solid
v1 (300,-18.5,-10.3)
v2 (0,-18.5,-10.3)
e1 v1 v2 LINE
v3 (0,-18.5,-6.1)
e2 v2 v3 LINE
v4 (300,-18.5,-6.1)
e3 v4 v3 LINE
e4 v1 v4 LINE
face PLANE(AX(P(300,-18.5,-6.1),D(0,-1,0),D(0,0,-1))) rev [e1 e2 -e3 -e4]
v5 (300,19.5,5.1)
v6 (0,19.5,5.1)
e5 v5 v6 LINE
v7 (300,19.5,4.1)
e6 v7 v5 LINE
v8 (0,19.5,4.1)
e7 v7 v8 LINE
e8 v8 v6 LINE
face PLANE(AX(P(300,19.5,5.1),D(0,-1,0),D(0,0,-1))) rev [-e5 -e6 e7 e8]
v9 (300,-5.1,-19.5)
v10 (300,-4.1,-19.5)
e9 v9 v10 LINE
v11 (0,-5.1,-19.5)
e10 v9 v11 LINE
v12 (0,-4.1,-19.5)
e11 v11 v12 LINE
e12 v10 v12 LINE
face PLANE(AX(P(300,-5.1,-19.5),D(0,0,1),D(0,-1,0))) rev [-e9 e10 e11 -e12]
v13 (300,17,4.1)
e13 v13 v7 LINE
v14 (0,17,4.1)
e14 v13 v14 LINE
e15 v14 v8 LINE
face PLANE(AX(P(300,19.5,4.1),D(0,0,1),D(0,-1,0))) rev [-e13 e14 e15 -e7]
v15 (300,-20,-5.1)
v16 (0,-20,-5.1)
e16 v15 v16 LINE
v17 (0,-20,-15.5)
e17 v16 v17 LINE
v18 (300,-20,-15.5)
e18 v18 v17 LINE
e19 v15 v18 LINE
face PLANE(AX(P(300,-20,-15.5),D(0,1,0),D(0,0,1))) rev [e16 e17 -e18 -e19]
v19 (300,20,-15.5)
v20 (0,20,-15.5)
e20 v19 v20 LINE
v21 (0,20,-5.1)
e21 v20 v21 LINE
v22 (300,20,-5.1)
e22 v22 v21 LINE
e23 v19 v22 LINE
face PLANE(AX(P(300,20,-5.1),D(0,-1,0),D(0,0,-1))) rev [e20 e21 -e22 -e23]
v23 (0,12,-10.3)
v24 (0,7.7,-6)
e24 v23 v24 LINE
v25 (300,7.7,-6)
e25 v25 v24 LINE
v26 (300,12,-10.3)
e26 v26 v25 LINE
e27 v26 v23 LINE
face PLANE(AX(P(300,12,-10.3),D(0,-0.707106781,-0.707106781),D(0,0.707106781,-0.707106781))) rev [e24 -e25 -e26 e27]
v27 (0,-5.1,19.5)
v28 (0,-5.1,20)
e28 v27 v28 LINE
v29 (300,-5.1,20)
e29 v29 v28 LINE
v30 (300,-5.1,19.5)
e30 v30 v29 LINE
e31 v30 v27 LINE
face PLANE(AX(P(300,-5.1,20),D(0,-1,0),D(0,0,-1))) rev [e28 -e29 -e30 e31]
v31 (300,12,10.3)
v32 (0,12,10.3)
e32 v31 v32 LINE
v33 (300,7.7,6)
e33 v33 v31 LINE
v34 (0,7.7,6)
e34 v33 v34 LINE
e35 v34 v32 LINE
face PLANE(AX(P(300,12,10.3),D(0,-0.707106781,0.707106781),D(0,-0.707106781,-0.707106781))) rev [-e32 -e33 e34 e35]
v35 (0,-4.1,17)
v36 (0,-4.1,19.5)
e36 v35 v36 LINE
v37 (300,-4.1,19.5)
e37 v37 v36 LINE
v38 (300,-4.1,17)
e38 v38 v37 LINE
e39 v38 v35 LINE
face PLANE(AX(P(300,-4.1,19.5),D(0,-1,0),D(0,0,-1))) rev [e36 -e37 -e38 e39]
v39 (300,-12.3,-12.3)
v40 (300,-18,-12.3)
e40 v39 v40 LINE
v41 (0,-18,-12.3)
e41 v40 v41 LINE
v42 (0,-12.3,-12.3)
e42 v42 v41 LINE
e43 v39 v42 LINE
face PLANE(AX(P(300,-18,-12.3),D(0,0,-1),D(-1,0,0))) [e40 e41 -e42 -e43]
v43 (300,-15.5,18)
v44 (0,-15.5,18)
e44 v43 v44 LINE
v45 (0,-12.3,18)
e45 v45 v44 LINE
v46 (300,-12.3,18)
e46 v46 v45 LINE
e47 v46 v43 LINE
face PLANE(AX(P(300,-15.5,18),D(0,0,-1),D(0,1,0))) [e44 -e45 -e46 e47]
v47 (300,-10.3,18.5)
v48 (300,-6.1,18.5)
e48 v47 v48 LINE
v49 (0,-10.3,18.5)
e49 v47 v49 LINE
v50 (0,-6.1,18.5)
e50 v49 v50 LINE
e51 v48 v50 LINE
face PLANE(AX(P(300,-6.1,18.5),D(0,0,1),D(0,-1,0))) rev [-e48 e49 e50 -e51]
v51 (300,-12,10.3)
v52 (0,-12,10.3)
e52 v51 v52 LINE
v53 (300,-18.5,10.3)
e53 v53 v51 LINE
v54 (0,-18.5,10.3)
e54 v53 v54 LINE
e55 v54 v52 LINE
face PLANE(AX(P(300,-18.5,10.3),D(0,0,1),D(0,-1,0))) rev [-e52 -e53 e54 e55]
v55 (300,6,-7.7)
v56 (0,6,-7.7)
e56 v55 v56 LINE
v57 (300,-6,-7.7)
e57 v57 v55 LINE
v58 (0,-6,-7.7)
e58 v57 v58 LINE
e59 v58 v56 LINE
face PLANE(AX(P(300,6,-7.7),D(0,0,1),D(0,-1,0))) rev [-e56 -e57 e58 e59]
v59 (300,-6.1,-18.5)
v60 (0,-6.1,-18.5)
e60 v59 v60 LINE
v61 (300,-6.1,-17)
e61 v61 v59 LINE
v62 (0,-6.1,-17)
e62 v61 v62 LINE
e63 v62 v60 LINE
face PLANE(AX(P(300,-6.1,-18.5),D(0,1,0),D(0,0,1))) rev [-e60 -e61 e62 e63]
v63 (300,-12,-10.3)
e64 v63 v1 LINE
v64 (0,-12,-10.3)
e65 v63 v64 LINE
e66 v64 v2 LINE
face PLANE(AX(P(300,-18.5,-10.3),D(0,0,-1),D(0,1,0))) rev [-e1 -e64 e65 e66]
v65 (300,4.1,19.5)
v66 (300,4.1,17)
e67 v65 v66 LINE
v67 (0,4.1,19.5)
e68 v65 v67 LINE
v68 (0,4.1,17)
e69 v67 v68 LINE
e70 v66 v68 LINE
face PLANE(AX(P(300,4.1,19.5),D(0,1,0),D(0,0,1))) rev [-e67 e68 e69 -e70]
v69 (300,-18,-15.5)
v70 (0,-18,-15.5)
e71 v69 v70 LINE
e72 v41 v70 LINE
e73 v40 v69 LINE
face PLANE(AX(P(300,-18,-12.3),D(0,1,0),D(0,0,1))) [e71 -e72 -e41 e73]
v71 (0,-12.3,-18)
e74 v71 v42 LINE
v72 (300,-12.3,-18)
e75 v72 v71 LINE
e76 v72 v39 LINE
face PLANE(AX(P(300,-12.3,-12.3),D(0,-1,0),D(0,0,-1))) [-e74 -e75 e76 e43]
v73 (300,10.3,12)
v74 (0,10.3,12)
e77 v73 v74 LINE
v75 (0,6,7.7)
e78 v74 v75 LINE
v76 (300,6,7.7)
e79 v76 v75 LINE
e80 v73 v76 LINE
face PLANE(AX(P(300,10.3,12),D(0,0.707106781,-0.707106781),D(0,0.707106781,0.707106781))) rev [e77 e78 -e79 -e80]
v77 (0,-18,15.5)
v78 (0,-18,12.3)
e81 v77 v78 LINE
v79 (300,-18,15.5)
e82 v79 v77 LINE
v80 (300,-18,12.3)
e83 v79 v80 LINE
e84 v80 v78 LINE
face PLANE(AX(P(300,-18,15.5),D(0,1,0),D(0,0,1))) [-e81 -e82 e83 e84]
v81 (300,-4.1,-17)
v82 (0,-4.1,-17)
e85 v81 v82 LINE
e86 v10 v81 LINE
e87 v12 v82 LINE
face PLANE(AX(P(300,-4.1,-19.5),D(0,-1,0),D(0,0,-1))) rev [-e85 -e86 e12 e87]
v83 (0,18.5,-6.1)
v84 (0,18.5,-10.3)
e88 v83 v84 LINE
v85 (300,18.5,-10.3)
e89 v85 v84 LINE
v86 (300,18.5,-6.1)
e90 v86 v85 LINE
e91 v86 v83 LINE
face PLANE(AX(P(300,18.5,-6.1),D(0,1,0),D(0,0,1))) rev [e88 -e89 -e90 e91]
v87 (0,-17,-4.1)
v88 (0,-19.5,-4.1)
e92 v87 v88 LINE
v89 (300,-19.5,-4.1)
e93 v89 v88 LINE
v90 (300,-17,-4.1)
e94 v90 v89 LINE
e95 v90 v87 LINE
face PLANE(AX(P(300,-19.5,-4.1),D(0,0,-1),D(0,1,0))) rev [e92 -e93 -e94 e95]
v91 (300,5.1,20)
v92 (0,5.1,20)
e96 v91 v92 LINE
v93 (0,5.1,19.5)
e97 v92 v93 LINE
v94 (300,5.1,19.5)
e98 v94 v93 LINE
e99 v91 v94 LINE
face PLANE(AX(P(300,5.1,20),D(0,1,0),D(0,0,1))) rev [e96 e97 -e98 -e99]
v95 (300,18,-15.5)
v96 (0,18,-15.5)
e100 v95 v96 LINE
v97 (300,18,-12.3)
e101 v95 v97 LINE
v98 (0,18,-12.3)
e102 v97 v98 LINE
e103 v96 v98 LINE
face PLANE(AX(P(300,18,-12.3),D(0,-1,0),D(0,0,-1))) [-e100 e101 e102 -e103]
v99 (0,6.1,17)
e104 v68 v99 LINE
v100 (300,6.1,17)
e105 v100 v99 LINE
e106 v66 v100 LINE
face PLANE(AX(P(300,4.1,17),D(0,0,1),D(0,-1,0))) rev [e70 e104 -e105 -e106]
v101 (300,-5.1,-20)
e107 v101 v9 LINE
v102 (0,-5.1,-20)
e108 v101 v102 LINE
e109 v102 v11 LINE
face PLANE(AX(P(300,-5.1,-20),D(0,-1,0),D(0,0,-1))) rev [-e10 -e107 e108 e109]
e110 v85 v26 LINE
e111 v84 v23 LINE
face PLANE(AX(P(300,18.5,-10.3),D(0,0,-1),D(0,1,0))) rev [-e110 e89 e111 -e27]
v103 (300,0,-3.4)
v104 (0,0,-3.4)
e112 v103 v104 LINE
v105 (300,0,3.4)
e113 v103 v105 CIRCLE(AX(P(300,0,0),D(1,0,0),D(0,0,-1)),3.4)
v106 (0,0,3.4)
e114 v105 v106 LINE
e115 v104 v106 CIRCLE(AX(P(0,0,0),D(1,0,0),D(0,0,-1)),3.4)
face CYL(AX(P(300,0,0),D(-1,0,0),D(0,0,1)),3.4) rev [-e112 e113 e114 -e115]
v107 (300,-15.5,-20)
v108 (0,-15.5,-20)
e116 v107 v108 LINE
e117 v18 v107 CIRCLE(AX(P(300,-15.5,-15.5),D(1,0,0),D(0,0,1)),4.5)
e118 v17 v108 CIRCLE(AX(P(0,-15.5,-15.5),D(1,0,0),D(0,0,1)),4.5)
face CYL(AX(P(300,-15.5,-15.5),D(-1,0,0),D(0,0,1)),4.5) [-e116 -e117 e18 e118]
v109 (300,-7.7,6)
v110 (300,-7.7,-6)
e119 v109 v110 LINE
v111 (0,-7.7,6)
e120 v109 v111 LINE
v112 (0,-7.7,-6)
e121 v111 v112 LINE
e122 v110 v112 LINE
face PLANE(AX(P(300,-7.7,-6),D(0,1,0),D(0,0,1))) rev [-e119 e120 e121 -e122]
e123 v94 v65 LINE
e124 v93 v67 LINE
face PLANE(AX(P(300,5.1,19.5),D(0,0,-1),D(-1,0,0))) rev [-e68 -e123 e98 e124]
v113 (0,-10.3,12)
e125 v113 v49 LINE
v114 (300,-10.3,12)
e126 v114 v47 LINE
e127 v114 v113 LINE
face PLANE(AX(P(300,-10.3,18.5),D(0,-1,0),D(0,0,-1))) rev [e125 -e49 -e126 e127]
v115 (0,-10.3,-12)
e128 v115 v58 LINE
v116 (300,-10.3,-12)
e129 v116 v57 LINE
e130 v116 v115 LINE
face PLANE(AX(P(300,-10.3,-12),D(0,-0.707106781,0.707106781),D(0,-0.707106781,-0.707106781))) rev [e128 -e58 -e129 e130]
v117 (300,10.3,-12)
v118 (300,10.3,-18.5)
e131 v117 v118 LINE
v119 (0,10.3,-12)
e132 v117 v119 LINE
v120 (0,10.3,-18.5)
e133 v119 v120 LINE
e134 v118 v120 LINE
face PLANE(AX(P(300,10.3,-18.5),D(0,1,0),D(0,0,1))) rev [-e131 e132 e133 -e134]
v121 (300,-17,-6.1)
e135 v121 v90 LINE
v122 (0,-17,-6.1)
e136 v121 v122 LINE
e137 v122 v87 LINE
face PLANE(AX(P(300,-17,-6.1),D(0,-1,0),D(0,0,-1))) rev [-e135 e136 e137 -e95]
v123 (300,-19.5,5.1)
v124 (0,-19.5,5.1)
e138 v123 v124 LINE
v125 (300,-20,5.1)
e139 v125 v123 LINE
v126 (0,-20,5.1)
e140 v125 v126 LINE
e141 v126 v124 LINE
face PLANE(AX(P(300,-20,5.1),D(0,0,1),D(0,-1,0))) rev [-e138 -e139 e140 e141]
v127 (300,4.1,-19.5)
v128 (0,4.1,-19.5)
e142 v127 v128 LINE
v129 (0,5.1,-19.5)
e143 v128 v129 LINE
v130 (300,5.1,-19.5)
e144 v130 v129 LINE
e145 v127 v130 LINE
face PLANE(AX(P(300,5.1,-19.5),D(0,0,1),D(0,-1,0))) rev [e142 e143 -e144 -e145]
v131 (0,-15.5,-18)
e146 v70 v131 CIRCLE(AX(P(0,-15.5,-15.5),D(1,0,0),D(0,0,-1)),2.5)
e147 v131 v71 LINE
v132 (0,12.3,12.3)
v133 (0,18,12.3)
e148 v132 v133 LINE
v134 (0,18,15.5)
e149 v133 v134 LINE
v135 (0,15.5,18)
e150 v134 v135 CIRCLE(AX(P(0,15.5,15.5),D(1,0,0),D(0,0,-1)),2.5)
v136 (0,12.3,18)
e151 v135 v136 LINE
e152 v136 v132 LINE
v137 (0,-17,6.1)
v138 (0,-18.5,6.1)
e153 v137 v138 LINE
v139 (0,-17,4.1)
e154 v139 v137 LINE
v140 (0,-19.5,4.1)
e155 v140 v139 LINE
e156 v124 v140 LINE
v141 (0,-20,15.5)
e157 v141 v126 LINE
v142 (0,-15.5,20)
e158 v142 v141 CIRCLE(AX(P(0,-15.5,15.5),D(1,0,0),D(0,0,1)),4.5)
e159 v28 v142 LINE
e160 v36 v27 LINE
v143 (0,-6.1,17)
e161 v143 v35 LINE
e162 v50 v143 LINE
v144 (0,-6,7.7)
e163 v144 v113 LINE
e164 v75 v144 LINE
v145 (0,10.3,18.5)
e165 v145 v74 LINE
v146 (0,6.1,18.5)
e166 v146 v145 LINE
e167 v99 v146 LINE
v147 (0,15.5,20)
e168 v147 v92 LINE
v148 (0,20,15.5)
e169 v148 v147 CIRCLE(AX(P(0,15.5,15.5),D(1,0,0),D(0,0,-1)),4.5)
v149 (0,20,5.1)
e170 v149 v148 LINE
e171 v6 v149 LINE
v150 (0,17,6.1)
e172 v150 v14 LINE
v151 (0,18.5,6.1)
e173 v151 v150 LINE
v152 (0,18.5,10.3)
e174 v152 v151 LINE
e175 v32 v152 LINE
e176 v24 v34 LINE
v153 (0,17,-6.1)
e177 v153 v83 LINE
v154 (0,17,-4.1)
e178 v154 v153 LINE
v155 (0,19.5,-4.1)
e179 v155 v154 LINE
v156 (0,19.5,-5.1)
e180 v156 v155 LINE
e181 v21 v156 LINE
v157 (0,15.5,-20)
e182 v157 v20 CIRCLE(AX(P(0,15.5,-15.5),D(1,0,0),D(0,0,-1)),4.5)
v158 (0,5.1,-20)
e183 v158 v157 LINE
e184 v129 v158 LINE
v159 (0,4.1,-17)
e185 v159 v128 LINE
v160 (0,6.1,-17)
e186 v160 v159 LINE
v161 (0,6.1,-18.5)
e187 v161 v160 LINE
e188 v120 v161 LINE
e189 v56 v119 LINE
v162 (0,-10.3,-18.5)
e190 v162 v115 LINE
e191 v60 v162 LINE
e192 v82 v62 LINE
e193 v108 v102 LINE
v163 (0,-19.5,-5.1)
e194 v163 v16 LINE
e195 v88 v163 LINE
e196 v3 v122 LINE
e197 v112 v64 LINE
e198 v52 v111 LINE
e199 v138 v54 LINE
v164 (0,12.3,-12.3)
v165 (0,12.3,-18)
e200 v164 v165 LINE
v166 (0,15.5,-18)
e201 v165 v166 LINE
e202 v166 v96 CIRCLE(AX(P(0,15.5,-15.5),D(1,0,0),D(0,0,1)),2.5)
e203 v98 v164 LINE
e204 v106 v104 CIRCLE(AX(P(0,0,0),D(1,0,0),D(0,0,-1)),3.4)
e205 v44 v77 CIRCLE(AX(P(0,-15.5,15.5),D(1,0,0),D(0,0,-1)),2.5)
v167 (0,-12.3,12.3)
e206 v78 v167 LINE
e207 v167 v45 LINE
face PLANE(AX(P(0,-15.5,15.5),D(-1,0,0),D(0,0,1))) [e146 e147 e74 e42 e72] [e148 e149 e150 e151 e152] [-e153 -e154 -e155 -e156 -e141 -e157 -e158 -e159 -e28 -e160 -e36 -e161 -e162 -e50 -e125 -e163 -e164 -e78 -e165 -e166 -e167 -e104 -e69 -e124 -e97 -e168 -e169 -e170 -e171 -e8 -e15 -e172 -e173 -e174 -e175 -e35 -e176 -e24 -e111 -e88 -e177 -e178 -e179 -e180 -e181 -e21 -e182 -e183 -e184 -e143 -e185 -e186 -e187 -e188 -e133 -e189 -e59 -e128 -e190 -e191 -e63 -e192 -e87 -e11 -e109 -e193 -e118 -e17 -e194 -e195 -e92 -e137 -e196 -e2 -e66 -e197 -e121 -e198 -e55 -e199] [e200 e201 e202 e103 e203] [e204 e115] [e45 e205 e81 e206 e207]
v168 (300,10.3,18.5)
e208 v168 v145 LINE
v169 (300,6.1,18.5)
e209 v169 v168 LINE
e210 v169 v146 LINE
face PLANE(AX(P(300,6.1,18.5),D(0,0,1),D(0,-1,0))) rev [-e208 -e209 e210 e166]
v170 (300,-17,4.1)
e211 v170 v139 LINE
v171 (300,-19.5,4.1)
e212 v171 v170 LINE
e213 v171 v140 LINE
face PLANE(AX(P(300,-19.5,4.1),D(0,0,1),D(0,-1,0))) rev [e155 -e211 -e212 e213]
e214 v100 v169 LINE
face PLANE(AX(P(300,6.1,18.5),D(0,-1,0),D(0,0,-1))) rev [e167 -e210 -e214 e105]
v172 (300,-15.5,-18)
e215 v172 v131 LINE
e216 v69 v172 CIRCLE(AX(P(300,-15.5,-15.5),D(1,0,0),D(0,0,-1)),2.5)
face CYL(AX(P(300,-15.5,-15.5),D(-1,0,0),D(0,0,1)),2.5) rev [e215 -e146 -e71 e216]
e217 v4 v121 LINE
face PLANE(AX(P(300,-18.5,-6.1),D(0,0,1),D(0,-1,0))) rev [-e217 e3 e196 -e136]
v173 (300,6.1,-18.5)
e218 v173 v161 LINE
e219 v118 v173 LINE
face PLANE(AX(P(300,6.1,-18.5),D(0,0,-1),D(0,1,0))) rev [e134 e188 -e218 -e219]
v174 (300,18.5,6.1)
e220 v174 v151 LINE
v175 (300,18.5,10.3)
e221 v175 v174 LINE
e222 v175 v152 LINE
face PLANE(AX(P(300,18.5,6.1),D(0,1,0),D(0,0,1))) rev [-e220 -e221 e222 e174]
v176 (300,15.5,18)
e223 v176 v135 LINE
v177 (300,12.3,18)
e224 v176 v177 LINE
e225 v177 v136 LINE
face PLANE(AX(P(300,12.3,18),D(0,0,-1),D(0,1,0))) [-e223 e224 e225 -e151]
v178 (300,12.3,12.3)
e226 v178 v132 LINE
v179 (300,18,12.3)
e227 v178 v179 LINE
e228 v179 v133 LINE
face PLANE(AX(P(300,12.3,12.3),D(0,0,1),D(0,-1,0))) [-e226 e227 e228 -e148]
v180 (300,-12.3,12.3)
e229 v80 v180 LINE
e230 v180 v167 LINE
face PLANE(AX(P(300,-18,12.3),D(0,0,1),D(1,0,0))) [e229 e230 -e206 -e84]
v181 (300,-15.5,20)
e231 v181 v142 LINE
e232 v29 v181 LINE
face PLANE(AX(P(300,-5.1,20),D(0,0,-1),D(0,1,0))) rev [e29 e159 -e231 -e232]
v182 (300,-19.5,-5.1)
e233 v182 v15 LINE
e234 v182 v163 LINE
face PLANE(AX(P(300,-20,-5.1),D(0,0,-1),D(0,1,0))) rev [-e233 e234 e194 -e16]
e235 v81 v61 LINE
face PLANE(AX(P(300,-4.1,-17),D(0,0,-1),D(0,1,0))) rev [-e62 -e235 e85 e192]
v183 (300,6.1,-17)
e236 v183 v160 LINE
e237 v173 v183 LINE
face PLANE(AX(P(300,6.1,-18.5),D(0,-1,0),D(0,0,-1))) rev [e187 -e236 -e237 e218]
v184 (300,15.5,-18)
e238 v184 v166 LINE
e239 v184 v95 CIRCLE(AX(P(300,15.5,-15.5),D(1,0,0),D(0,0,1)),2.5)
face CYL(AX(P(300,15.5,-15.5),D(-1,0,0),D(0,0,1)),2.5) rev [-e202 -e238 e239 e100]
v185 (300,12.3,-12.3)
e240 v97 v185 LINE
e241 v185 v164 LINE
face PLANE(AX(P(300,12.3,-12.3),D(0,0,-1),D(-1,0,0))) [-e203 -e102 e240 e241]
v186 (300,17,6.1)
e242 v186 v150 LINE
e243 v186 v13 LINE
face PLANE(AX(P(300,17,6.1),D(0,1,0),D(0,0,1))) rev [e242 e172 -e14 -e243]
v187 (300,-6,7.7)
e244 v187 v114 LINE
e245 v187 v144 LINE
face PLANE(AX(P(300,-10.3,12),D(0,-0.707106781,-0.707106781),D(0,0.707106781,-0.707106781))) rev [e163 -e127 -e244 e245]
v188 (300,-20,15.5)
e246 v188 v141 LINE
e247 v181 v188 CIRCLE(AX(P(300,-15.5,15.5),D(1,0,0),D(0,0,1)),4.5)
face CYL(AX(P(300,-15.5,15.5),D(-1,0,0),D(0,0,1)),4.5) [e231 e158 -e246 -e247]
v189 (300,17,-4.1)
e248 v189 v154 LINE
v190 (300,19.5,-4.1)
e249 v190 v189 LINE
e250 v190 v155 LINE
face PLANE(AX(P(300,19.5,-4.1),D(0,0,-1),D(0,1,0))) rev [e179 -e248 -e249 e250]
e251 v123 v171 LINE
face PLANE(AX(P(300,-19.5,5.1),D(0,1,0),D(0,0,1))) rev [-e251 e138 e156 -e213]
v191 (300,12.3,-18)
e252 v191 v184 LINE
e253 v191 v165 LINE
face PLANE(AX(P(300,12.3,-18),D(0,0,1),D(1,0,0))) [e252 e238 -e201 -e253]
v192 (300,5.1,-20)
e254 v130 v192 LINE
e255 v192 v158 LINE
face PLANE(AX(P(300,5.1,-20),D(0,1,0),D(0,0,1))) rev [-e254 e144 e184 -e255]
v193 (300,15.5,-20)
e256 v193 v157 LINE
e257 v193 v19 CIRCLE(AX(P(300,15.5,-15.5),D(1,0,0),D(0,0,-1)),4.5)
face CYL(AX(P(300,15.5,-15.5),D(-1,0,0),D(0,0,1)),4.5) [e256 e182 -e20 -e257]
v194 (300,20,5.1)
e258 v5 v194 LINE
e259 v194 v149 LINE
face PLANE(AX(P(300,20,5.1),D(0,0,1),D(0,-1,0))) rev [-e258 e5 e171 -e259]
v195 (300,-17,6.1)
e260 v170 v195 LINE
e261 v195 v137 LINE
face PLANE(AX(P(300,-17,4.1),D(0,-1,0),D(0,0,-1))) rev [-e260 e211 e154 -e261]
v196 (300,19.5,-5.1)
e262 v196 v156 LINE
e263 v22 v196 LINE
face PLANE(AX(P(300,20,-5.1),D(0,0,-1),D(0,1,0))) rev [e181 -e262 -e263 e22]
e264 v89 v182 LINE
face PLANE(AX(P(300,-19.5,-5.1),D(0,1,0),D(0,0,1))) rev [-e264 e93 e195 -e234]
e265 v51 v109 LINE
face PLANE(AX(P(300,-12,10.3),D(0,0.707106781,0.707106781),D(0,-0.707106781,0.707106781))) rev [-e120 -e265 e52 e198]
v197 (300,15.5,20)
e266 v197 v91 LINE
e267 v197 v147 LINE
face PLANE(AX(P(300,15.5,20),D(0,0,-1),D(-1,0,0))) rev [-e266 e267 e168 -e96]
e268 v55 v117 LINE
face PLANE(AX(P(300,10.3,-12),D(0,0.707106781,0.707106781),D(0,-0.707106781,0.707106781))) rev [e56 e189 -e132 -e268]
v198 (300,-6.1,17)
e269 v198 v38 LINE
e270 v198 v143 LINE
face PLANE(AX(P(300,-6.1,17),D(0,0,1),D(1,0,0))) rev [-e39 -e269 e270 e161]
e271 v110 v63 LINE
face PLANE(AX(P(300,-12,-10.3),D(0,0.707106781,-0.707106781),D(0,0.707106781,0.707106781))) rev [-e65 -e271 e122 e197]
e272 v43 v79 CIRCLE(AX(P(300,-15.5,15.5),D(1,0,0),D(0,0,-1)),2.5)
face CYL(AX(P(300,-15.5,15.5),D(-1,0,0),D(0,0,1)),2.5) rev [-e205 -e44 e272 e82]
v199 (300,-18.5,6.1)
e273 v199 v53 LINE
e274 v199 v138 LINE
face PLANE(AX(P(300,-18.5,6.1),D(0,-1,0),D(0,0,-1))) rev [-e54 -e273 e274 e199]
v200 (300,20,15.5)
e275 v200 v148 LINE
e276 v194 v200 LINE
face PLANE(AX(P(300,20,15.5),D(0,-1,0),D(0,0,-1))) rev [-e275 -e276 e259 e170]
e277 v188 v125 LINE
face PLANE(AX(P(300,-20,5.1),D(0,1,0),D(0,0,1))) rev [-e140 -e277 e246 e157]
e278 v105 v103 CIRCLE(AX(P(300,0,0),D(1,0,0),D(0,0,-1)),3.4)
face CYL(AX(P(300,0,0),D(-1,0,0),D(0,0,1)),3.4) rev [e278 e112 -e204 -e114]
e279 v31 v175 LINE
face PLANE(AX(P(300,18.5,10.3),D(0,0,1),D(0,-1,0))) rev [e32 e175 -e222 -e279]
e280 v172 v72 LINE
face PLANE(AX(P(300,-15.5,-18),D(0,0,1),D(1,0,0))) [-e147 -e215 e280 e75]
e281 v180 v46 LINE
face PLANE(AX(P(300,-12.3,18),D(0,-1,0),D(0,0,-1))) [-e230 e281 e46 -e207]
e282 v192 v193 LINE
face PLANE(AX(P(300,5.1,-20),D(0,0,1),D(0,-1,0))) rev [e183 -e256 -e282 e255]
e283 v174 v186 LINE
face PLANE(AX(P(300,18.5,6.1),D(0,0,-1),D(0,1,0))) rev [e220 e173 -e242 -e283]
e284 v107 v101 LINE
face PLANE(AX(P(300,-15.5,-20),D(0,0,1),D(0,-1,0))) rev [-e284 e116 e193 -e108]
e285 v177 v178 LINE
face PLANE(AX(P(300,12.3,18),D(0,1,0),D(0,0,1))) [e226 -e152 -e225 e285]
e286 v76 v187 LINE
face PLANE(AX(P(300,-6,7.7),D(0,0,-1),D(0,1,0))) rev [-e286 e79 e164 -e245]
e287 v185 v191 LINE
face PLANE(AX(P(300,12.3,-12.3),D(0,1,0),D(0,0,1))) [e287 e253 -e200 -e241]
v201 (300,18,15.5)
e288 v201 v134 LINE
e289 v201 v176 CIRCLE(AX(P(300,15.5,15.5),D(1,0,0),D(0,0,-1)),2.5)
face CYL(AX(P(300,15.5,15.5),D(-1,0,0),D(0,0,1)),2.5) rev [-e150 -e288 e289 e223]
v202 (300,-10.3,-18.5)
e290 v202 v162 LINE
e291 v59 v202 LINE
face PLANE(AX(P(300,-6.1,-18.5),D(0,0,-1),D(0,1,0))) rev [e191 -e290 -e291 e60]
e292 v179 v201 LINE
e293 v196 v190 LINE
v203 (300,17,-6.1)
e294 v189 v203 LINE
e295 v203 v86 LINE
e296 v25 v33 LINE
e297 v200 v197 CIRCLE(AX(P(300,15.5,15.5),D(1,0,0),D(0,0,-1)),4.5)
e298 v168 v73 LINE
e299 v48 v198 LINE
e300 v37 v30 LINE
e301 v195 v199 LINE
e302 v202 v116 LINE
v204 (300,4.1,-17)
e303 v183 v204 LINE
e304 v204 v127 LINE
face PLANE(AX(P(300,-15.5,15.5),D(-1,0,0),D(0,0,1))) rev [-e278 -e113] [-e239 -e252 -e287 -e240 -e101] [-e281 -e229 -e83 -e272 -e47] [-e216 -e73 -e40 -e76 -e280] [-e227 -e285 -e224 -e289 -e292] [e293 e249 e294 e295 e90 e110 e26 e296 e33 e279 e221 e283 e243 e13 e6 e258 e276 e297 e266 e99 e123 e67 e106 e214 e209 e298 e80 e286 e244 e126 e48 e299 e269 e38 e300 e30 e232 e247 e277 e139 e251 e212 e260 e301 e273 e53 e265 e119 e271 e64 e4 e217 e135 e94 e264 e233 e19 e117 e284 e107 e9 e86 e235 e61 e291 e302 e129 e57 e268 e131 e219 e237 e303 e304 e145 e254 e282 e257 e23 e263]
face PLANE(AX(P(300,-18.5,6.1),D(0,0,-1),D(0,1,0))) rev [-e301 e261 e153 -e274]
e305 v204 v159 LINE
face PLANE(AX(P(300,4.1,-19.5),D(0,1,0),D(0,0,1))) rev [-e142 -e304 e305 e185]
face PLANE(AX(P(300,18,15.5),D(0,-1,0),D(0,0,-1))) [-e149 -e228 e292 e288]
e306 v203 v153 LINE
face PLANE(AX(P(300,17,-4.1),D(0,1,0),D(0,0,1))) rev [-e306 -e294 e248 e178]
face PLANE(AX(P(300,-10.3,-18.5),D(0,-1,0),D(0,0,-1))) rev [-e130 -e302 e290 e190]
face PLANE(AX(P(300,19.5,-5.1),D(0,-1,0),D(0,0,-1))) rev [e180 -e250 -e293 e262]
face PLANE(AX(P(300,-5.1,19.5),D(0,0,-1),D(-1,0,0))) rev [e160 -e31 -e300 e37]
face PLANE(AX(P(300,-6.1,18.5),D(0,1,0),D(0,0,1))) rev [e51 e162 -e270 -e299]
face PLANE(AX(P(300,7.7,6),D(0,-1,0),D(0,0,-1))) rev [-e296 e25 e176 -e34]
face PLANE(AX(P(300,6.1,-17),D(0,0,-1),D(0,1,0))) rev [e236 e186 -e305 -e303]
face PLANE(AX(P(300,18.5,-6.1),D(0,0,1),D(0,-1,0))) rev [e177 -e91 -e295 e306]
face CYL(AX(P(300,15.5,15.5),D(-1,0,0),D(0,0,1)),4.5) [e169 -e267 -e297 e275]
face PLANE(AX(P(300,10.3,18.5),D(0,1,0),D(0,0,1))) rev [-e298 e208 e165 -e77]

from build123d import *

# Parameters (mm, degrees)
SKETCH1_R                                = 3.4
ALUMINUM_PROFILE_40_X_40B_X_R4_5_1_DEPTH = 300


with BuildPart() as part:
    # Sketch1 → Aluminum profile 40 X 40B X R4.5(1) (new body)
    with BuildSketch(Plane.YZ):
        with BuildLine():
            Line((-5.1, 20), (-5.1, 19.5))
            Line((-5.1, 19.5), (-4.1, 19.5))
            Line((-4.1, 19.5), (-4.1, 17))
            Line((-4.1, 17), (-6.1, 17))
            Line((-6.1, 17), (-6.1, 18.5))
            Line((-6.1, 18.5), (-10.3, 18.5))
            Line((-10.3, 18.5), (-10.3, 12))
            Line((-10.3, 12), (-6, 7.7))
            Line((-6, 7.7), (6, 7.7))
            Line((6, 7.7), (10.3, 12))
            Line((10.3, 12), (10.3, 18.5))
            Line((10.3, 18.5), (6.1, 18.5))
            Line((6.1, 18.5), (6.1, 17))
            Line((6.1, 17), (4.1, 17))
            Line((4.1, 17), (4.1, 19.5))
            Line((4.1, 19.5), (5.1, 19.5))
            Line((5.1, 19.5), (5.1, 20))
            Line((5.1, 20), (15.5, 20))
            ThreePointArc((15.5, 20), (18.681980515, 18.681980515), (20, 15.5))
            Line((20, 15.5), (20, 5.1))
            Line((20, 5.1), (19.5, 5.1))
            Line((19.5, 5.1), (19.5, 4.1))
            Line((19.5, 4.1), (17, 4.1))
            Line((17, 4.1), (17, 6.1))
            Line((17, 6.1), (18.5, 6.1))
            Line((18.5, 6.1), (18.5, 10.3))
            Line((18.5, 10.3), (12, 10.3))
            Line((12, 10.3), (7.7, 6))
            Line((7.7, 6), (7.7, -6))
            Line((7.7, -6), (12, -10.3))
            Line((12, -10.3), (18.5, -10.3))
            Line((18.5, -10.3), (18.5, -6.1))
            Line((18.5, -6.1), (17, -6.1))
            Line((17, -6.1), (17, -4.1))
            Line((17, -4.1), (19.5, -4.1))
            Line((19.5, -4.1), (19.5, -5.1))
            Line((19.5, -5.1), (20, -5.1))
            Line((20, -5.1), (20, -15.5))
            ThreePointArc((20, -15.5), (18.681980515, -18.681980515), (15.5, -20))
            Line((15.5, -20), (5.1, -20))
            Line((5.1, -20), (5.1, -19.5))
            Line((5.1, -19.5), (4.1, -19.5))
            Line((4.1, -19.5), (4.1, -17))
            Line((4.1, -17), (6.1, -17))
            Line((6.1, -17), (6.1, -18.5))
            Line((6.1, -18.5), (10.3, -18.5))
            Line((10.3, -18.5), (10.3, -12))
            Line((10.3, -12), (6, -7.7))
            Line((6, -7.7), (-6, -7.7))
            Line((-6, -7.7), (-10.3, -12))
            Line((-10.3, -12), (-10.3, -18.5))
            Line((-10.3, -18.5), (-6.1, -18.5))
            Line((-6.1, -18.5), (-6.1, -17))
            Line((-6.1, -17), (-4.1, -17))
            Line((-4.1, -17), (-4.1, -19.5))
            Line((-4.1, -19.5), (-5.1, -19.5))
            Line((-5.1, -19.5), (-5.1, -20))
            Line((-5.1, -20), (-15.5, -20))
            ThreePointArc((-15.5, -20), (-18.681980515, -18.681980515), (-20, -15.5))
            Line((-20, -15.5), (-20, -5.1))
            Line((-20, -5.1), (-19.5, -5.1))
            Line((-19.5, -5.1), (-19.5, -4.1))
            Line((-19.5, -4.1), (-17, -4.1))
            Line((-17, -4.1), (-17, -6.1))
            Line((-17, -6.1), (-18.5, -6.1))
            Line((-18.5, -6.1), (-18.5, -10.3))
            Line((-18.5, -10.3), (-12, -10.3))
            Line((-12, -10.3), (-7.7, -6))
            Line((-7.7, -6), (-7.7, 6))
            Line((-7.7, 6), (-12, 10.3))
            Line((-12, 10.3), (-18.5, 10.3))
            Line((-18.5, 10.3), (-18.5, 6.1))
            Line((-18.5, 6.1), (-17, 6.1))
            Line((-17, 6.1), (-17, 4.1))
            Line((-17, 4.1), (-19.5, 4.1))
            Line((-19.5, 4.1), (-19.5, 5.1))
            Line((-19.5, 5.1), (-20, 5.1))
            Line((-20, 5.1), (-20, 15.5))
            ThreePointArc((-20, 15.5), (-18.681980515, 18.681980515), (-15.5, 20))
            Line((-15.5, 20), (-5.1, 20))
        make_face()
        Circle(SKETCH1_R, mode=Mode.SUBTRACT)
        with BuildLine():
            Line((12.3, 18), (15.5, 18))
            ThreePointArc((15.5, 18), (17.267766953, 17.267766953), (18, 15.5))
            Line((18, 15.5), (18, 12.3))
            Line((18, 12.3), (12.3, 12.3))
            Line((12.3, 12.3), (12.3, 18))
        make_face(mode=Mode.SUBTRACT)
        with BuildLine():
            Line((-15.5, 18), (-12.3, 18))
            Line((-12.3, 18), (-12.3, 12.3))
            Line((-12.3, 12.3), (-18, 12.3))
            Line((-18, 12.3), (-18, 15.5))
            ThreePointArc((-18, 15.5), (-17.267766953, 17.267766953), (-15.5, 18))
        make_face(mode=Mode.SUBTRACT)
        with BuildLine():
            Line((-18, -12.3), (-12.3, -12.3))
            Line((-12.3, -12.3), (-12.3, -18))
            Line((-12.3, -18), (-15.5, -18))
            ThreePointArc((-15.5, -18), (-17.267766953, -17.267766953), (-18, -15.5))
            Line((-18, -15.5), (-18, -12.3))
        make_face(mode=Mode.SUBTRACT)
        with BuildLine():
            Line((12.3, -12.3), (18, -12.3))
            Line((18, -12.3), (18, -15.5))
            ThreePointArc((18, -15.5), (17.267766953, -17.267766953), (15.5, -18))
            Line((15.5, -18), (12.3, -18))
            Line((12.3, -18), (12.3, -12.3))
        make_face(mode=Mode.SUBTRACT)
    extrude(amount=ALUMINUM_PROFILE_40_X_40B_X_R4_5_1_DEPTH)


solid = part.part
